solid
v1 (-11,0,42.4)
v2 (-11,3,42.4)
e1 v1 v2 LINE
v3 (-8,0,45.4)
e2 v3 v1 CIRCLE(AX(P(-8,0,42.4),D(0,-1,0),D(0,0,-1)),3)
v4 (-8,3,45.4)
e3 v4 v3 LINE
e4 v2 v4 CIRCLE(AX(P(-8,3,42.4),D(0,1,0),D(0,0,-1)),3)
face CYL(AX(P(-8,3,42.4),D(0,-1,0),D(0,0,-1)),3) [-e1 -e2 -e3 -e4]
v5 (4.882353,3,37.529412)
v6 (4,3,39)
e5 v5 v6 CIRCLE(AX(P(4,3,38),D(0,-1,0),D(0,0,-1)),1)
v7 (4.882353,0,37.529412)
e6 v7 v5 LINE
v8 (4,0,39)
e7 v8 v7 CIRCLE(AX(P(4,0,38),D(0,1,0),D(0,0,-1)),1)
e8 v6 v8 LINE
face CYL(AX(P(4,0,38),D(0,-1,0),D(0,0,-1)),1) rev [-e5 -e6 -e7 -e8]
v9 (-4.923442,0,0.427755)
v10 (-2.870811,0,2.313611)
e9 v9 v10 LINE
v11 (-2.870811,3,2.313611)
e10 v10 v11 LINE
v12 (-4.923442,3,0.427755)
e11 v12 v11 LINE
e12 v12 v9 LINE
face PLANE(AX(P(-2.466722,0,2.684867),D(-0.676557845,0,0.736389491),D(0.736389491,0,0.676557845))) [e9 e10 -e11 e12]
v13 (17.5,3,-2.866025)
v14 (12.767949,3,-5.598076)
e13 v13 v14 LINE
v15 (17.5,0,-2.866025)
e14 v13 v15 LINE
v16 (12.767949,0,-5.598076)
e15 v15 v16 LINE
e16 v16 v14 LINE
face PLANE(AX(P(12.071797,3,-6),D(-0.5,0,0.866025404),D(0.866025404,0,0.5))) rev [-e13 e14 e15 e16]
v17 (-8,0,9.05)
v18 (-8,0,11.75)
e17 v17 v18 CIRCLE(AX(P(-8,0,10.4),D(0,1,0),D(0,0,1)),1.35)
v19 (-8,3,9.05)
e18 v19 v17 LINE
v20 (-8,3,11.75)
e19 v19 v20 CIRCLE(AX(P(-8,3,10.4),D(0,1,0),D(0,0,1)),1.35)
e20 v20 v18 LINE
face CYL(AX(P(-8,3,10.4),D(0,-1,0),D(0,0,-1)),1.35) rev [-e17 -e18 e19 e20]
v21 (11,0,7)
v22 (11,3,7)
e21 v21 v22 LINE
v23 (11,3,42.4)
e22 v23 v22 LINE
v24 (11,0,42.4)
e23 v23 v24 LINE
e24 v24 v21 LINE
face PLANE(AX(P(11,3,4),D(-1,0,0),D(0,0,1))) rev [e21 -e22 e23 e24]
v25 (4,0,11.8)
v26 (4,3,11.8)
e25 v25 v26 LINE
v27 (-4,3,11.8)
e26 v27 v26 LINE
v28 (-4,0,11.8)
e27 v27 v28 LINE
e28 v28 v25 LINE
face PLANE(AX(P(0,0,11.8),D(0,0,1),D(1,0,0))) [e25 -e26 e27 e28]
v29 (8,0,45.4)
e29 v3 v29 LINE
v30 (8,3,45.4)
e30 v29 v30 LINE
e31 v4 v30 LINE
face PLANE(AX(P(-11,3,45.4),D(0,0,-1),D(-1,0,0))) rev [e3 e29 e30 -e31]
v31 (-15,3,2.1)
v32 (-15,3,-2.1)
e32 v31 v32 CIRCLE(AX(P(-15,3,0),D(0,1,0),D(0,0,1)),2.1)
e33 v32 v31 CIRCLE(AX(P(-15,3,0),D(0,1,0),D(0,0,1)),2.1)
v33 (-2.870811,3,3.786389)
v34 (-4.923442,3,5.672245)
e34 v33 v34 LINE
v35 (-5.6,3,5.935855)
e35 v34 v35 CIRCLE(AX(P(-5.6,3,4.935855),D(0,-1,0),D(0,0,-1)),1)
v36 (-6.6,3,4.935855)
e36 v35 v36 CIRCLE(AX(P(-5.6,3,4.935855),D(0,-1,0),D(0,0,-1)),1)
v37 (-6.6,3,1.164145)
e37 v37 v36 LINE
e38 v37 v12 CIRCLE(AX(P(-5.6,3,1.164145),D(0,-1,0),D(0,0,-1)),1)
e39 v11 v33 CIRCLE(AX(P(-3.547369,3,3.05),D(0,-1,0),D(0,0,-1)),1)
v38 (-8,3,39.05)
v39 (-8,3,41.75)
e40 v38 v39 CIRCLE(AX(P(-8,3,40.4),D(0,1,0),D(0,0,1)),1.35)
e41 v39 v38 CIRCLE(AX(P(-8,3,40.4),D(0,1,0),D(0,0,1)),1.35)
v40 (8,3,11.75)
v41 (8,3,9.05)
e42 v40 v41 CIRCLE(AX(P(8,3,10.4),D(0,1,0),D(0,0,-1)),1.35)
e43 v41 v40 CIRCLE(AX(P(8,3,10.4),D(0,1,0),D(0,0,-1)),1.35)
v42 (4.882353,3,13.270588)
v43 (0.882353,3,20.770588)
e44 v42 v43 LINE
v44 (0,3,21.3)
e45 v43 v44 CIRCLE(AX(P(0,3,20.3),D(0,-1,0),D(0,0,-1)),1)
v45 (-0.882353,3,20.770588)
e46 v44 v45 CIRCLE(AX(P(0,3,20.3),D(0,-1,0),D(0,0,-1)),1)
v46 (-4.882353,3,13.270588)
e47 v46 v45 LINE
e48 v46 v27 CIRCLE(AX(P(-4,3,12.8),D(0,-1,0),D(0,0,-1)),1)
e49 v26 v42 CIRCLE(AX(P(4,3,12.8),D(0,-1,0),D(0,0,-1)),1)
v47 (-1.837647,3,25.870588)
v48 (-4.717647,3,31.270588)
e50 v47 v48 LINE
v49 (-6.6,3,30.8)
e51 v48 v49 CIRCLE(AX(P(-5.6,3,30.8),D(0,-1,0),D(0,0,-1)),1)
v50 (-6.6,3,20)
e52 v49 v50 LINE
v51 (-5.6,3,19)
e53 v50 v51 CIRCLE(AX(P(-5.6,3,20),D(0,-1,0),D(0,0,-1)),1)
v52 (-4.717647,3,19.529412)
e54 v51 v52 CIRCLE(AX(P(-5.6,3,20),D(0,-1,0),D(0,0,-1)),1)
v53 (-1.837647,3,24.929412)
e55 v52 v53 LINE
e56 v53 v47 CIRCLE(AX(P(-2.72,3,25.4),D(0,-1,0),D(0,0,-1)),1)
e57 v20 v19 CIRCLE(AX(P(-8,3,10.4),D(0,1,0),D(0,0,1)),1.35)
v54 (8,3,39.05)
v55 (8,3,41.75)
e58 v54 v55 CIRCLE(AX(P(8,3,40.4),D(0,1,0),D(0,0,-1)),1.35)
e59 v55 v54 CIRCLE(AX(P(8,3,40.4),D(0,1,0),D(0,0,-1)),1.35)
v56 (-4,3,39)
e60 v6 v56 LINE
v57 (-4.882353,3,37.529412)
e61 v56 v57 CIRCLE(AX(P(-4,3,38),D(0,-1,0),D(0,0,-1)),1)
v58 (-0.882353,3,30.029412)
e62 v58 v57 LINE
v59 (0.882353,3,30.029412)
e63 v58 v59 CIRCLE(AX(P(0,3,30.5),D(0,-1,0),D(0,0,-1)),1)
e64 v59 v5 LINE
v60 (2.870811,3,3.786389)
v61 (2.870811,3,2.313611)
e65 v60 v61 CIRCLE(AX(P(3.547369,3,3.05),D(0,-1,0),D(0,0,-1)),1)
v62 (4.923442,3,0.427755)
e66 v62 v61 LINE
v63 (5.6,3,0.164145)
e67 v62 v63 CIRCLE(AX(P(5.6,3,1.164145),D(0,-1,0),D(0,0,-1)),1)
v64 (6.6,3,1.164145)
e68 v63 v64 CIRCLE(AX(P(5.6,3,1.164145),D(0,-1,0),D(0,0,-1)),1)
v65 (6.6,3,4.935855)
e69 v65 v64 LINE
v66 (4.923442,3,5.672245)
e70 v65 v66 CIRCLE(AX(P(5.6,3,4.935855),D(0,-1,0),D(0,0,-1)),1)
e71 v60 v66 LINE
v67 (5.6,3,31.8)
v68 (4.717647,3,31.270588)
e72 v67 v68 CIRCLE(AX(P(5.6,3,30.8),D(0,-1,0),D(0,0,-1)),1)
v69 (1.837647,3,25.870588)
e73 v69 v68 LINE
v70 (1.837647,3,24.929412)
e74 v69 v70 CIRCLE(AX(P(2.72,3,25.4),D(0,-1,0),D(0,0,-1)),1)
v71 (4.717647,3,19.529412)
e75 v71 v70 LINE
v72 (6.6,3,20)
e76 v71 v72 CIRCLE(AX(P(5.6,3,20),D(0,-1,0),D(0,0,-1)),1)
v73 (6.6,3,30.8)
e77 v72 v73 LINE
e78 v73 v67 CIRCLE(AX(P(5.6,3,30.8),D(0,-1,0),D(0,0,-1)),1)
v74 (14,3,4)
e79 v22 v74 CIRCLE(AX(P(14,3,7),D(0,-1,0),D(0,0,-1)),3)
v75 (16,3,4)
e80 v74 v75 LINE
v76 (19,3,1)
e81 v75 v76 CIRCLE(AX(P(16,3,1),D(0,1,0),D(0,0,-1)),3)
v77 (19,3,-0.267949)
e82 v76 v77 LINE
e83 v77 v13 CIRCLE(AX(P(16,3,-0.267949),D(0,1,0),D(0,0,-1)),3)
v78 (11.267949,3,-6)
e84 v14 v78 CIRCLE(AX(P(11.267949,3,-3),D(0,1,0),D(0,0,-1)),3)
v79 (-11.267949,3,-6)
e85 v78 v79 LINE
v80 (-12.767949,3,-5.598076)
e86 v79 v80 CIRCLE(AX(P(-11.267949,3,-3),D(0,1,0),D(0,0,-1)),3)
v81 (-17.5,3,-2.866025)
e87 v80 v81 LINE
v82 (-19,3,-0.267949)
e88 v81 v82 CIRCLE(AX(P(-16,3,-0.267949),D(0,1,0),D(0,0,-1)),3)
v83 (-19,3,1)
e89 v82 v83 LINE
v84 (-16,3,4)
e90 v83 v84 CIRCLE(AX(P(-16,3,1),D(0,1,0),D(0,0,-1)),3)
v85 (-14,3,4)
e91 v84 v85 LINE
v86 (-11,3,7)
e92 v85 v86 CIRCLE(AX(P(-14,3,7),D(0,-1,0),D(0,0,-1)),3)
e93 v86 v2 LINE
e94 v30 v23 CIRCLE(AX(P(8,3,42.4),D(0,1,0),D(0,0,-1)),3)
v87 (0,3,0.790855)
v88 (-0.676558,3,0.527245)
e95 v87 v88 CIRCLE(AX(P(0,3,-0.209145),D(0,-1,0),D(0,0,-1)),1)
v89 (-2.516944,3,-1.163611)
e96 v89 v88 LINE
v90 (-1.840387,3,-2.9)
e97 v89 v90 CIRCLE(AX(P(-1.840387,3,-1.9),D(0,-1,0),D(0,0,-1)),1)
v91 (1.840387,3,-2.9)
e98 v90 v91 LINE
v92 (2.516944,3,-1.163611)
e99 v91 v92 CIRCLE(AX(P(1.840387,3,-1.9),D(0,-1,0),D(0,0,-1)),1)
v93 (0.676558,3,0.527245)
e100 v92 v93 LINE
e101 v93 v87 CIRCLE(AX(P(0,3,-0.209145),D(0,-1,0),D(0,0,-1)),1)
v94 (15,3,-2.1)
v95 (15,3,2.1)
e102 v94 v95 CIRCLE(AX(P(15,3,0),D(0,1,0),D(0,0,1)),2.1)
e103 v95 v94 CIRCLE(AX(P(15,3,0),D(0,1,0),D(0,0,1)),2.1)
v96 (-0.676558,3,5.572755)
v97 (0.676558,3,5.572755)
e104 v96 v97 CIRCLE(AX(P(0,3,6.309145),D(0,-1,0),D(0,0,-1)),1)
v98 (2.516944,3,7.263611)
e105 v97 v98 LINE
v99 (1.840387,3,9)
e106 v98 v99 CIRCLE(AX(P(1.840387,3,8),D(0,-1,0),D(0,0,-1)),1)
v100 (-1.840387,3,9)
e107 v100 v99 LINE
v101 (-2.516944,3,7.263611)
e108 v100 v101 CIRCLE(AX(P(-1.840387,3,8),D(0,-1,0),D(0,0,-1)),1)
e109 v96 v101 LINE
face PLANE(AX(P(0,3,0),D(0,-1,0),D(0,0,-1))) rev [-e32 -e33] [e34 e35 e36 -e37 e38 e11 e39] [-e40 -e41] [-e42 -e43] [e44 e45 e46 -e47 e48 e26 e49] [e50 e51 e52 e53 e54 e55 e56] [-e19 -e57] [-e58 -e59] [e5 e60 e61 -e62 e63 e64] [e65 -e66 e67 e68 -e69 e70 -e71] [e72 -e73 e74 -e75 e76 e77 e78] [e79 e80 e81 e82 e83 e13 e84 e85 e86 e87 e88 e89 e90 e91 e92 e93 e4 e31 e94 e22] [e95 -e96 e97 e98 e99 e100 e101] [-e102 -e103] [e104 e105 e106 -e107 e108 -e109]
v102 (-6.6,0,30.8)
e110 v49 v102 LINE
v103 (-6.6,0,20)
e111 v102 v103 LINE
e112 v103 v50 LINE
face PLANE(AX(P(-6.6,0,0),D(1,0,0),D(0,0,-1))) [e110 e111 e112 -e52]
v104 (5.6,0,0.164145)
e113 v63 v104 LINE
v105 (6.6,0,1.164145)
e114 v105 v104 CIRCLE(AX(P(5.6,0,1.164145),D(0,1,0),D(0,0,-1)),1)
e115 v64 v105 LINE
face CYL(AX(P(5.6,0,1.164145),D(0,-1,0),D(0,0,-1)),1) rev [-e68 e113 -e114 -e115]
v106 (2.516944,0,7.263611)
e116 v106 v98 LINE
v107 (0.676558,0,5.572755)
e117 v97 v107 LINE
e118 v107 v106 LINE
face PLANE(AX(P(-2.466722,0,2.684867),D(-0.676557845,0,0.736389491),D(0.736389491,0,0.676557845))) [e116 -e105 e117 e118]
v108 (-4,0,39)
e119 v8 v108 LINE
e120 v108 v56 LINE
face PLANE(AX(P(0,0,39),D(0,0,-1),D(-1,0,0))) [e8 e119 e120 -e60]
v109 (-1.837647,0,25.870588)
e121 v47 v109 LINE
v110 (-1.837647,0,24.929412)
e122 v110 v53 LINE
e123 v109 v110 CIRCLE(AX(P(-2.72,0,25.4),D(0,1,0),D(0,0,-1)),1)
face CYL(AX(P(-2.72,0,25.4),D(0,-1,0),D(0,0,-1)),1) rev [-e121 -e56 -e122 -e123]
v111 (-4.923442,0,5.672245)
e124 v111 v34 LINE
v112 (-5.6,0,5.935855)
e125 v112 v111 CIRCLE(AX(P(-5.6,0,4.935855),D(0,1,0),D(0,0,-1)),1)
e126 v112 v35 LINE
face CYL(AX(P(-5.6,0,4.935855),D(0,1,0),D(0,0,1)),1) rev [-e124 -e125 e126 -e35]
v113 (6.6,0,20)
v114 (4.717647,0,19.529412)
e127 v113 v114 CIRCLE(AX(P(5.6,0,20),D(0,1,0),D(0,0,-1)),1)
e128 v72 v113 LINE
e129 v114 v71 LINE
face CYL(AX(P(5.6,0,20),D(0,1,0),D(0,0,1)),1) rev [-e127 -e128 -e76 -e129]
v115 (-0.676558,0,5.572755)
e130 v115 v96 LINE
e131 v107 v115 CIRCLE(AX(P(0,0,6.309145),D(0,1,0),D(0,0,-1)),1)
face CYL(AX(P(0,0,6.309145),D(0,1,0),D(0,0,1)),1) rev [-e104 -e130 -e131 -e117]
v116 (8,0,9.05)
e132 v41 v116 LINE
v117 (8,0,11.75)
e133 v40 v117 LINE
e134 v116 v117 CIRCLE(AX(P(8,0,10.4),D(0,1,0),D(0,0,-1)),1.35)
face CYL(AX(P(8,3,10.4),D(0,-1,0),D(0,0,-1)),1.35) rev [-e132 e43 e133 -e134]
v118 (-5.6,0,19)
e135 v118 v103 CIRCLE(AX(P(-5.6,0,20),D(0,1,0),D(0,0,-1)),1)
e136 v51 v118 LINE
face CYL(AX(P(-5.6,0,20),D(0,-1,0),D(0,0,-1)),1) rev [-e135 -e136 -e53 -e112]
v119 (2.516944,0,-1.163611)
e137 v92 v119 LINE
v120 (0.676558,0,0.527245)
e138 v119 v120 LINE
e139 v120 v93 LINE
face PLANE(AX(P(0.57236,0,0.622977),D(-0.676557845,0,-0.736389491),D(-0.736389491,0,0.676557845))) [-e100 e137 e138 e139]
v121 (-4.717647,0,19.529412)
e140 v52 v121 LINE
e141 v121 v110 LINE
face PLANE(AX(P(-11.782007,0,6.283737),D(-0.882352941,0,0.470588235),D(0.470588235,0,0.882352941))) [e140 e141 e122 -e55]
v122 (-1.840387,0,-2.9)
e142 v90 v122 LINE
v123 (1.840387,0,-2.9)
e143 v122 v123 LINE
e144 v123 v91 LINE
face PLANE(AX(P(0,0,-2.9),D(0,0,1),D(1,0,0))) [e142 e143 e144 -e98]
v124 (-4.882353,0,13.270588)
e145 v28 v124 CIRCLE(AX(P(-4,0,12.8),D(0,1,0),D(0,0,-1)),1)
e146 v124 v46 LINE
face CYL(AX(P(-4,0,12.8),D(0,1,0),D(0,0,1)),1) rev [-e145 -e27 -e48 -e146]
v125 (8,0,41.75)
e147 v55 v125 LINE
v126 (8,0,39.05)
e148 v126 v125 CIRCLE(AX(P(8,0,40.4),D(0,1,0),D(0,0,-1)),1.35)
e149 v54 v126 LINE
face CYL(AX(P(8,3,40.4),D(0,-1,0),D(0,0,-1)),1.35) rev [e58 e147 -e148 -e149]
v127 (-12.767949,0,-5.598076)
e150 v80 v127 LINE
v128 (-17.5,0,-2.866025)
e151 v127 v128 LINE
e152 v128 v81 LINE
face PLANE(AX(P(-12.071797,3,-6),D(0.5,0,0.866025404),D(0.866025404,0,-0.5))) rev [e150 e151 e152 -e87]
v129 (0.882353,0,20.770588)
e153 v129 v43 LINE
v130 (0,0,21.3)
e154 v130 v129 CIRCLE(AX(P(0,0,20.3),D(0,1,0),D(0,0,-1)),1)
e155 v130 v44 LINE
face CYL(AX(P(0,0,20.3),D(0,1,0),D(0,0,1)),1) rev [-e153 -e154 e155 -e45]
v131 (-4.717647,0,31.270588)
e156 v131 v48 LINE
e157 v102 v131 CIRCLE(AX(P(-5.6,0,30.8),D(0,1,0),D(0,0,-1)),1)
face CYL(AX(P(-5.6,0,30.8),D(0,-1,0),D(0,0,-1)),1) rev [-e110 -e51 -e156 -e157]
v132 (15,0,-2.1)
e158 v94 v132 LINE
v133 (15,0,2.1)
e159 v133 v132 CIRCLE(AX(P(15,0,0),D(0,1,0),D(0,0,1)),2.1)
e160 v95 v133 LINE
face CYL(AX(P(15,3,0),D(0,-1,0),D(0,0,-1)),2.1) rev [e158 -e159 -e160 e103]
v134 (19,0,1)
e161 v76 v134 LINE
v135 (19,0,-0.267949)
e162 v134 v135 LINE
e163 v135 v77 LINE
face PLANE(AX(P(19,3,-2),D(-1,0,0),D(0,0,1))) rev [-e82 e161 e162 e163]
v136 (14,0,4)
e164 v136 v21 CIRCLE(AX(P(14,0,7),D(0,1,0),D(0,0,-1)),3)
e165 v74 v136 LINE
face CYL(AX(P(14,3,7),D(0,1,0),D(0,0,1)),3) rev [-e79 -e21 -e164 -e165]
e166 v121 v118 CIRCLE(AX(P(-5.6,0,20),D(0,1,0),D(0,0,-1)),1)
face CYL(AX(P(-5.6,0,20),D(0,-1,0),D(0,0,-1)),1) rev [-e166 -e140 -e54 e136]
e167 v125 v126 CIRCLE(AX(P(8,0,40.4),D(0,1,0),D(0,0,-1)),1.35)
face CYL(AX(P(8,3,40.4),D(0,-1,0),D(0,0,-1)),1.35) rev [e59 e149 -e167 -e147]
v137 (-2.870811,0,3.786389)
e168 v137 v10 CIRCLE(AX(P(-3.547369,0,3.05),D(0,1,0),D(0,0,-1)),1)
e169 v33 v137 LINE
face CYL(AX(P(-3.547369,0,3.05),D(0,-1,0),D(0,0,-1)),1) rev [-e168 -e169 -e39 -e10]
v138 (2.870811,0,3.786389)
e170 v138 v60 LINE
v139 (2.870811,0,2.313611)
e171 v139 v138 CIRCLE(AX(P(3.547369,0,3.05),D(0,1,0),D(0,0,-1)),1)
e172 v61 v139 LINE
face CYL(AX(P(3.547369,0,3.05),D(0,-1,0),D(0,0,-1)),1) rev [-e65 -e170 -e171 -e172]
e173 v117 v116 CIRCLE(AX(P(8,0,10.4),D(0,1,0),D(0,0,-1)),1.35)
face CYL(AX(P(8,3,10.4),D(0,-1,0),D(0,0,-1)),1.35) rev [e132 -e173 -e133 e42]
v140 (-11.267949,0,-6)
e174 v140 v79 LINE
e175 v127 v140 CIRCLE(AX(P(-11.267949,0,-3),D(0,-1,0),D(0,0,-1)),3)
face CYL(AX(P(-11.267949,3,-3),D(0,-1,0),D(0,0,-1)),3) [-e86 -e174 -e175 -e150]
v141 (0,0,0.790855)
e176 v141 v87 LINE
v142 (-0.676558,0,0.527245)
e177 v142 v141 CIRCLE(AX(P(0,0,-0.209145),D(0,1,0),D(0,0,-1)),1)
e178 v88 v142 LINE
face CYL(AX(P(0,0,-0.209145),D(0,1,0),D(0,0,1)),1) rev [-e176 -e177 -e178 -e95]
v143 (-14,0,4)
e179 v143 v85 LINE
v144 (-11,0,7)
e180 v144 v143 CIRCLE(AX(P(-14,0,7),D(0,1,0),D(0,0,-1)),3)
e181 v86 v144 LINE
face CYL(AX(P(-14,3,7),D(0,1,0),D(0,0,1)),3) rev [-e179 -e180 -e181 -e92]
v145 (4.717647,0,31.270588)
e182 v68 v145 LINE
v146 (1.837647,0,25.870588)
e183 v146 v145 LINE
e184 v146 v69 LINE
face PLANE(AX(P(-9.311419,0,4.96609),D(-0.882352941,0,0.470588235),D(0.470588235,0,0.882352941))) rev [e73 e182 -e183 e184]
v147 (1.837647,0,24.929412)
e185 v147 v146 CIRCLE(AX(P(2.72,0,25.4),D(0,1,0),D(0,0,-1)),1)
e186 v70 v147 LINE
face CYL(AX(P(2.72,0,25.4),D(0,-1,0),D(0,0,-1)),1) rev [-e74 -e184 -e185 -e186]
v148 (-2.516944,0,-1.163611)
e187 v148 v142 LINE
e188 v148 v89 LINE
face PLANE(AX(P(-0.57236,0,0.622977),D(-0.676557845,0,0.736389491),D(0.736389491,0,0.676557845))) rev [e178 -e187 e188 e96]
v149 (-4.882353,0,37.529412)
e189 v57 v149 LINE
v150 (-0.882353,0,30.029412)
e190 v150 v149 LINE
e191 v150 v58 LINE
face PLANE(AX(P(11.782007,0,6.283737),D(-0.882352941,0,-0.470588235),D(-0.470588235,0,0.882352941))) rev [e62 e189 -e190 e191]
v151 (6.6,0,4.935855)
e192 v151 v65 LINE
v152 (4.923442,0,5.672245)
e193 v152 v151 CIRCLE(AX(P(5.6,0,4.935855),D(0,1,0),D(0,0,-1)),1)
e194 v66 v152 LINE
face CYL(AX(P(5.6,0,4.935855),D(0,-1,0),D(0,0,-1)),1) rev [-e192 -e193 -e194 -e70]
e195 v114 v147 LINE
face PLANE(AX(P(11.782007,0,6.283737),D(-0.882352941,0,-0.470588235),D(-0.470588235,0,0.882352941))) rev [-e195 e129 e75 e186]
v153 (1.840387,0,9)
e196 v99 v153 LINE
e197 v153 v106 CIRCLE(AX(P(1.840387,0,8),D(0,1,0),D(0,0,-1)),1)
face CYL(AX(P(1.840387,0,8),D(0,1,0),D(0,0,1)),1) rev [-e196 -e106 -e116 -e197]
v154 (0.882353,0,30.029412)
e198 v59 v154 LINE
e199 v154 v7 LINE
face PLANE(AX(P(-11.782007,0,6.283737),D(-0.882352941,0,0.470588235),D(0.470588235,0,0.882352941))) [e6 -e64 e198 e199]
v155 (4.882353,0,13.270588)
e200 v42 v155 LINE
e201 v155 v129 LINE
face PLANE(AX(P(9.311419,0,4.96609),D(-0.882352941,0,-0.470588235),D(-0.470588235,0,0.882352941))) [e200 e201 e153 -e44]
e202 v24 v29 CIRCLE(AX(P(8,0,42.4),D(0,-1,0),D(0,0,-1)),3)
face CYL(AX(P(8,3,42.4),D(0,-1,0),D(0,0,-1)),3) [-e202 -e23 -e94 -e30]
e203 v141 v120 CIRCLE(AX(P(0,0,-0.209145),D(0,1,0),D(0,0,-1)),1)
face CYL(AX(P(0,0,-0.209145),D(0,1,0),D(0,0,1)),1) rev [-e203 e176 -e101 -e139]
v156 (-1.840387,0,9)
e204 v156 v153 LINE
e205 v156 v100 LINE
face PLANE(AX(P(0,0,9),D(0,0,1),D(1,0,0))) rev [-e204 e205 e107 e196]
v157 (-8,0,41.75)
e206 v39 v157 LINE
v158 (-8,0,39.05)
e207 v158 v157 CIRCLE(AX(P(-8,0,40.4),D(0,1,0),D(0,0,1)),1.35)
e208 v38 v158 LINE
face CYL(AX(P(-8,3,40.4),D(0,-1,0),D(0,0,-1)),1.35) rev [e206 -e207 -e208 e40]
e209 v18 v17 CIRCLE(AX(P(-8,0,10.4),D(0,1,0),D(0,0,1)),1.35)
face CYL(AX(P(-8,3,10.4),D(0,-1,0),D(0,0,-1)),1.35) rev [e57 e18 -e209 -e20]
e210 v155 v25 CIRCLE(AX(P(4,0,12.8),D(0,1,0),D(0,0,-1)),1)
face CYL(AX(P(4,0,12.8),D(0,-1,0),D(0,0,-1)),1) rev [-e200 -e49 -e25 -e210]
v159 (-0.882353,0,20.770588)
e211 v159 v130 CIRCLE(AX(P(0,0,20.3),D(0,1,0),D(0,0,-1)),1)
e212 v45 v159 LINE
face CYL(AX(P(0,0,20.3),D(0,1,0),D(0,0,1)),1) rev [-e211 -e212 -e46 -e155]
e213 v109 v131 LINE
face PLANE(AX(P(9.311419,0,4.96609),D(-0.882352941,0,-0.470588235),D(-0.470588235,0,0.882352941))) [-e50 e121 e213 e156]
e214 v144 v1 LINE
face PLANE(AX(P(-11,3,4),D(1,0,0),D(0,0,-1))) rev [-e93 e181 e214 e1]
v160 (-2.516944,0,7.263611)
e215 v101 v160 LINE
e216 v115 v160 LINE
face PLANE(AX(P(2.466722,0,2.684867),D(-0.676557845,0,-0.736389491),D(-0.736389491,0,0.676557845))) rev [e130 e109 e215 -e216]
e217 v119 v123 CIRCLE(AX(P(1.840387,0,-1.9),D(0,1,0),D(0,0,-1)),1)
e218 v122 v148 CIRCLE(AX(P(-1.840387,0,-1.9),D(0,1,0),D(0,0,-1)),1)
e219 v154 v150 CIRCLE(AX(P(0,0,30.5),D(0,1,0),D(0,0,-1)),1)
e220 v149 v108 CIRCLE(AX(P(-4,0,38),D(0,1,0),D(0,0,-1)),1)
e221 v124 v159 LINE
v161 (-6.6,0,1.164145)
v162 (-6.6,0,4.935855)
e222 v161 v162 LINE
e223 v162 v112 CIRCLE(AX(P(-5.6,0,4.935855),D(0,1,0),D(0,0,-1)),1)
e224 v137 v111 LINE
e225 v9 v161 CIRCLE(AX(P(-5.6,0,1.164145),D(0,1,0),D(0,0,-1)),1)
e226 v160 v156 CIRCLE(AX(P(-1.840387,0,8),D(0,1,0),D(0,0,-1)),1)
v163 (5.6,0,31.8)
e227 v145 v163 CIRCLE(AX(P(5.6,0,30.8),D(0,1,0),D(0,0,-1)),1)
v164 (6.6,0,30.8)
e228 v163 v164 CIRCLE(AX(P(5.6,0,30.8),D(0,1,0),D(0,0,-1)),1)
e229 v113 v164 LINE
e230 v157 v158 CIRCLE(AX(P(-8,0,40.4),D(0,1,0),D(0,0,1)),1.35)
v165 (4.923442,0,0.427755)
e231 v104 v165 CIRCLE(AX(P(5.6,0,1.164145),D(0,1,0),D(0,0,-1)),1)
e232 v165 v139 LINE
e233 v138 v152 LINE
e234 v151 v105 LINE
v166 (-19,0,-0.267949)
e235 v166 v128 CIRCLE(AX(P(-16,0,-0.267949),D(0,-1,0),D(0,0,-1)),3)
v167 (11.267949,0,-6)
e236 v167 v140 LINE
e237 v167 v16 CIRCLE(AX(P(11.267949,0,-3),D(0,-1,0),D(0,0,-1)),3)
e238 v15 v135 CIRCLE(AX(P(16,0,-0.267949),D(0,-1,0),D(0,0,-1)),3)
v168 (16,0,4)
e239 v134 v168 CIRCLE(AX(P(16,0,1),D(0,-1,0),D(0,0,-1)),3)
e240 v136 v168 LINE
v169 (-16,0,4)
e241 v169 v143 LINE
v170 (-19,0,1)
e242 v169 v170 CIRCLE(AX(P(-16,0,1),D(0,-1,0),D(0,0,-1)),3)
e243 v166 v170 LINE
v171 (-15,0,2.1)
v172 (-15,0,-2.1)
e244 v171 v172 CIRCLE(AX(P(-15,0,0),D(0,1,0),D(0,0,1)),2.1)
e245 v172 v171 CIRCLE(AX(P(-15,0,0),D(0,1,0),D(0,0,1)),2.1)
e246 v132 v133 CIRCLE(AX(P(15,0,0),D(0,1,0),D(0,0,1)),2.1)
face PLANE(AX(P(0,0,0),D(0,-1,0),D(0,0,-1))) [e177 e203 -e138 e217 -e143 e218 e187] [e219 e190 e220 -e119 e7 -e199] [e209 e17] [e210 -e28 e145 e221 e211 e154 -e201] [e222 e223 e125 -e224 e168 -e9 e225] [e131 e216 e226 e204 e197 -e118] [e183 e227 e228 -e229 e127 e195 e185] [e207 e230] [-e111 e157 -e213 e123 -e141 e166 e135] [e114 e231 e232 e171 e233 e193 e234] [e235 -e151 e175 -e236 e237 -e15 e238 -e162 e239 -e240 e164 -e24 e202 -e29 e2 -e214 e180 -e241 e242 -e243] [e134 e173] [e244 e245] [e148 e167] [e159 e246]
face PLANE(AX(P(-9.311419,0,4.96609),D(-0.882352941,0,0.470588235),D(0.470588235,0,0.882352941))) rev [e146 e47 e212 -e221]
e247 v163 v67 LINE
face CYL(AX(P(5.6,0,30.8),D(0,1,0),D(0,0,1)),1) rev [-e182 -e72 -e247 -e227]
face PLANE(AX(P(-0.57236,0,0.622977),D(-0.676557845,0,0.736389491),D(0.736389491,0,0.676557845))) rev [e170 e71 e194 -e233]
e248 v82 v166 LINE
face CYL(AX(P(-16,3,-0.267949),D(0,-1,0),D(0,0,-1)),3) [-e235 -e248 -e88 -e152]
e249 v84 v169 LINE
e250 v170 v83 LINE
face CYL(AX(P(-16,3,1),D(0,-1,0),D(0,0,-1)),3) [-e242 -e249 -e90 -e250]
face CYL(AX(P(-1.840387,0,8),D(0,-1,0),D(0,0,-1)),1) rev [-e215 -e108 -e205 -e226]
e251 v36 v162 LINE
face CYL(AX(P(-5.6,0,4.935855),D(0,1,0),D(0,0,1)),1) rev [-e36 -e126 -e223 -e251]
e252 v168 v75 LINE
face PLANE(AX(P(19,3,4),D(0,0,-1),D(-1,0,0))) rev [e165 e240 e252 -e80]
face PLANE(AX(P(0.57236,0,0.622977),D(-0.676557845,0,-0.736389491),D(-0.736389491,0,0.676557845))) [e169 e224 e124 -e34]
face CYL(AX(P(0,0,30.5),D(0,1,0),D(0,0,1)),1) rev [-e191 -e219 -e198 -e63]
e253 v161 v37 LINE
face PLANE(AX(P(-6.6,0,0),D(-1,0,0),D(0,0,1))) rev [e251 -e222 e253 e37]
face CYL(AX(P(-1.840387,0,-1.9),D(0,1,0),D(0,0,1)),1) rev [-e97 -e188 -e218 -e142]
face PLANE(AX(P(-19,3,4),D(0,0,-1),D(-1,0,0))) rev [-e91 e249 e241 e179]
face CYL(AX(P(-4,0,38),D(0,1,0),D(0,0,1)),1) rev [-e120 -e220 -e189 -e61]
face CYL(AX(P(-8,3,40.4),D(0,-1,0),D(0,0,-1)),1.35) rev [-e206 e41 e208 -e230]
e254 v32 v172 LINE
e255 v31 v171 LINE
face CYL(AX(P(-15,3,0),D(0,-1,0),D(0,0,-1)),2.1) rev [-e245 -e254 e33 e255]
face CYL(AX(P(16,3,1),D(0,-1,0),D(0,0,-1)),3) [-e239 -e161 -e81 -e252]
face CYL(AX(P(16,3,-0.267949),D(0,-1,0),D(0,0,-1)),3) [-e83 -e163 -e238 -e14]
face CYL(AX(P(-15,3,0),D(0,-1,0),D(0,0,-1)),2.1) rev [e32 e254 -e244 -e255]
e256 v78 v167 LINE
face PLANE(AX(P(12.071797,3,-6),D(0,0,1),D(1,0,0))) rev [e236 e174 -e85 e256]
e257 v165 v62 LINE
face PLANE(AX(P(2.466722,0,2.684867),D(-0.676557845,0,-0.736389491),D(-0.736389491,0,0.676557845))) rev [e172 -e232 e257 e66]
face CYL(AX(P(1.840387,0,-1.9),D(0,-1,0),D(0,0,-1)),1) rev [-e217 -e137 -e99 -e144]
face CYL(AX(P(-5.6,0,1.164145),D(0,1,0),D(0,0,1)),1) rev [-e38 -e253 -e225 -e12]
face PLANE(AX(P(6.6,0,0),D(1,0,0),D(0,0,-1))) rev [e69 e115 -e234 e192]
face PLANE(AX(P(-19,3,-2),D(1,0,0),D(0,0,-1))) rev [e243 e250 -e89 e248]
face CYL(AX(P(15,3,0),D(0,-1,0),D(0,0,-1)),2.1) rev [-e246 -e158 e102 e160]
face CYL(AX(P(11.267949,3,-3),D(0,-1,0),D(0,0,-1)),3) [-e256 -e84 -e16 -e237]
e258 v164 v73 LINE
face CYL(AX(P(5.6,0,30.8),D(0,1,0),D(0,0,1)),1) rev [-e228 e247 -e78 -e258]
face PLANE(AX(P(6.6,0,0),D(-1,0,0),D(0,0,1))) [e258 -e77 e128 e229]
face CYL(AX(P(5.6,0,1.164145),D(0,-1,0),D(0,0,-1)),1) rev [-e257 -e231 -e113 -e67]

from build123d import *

# Parameters (mm, degrees)
SKETCH1_R              = 2.1
SKETCH1_R_2            = 1.35
BOSS_EXTRUDE1_DEPTH    = 3
CUT_EXTRUDE1_DEPTH     = 50.306794664
R3_OUTER_EDGE_FILLET_R = 3
R1_CUTOUT_FILLET_R     = 1


with BuildPart() as part:
    # Sketch1 → Boss-Extrude1 (new body)
    with BuildSketch(Plane(origin=(0, 0, 0), x_dir=(1, 0, 0), z_dir=(0, 1, 0))):
        Polygon((-12.07179677, 6), (-19, 2), (-19, -4), (-11, -4), (-11, -45.4), (11, -45.4), (11, -4), (19, -4), (19, 2), (12.07179677, 6), align=None)
        with Locations(Location((-15, 0, 0), (0, 0, 270))):
            Circle(SKETCH1_R, mode=Mode.SUBTRACT)
        with Locations(Location((15, 0, 0), (0, 0, 270))):
            Circle(SKETCH1_R, mode=Mode.SUBTRACT)
        with Locations(Location((-8, -10.4, 0), (0, 0, 270))):
            Circle(SKETCH1_R_2, mode=Mode.SUBTRACT)
        with Locations(Location((-8, -40.4, 0), (0, 0, 270))):
            Circle(SKETCH1_R_2, mode=Mode.SUBTRACT)
        with Locations(Location((8, -10.4, 0), (0, 0, 90))):
            Circle(SKETCH1_R_2, mode=Mode.SUBTRACT)
        with Locations(Location((8, -40.4, 0), (0, 0, 90))):
            Circle(SKETCH1_R_2, mode=Mode.SUBTRACT)
    extrude(amount=BOSS_EXTRUDE1_DEPTH)

    # Sketch2 → Cut-Extrude1 (cut, through all)
    with BuildSketch(Plane(origin=(0, 3, 0), x_dir=(1, 0, 0), z_dir=(0, 1, 0))):
        Polygon((-6.6, 1.112582185), (-6.6, -7.212582185), (-2.069298303, -3.05), align=None)
        Polygon((-4.406892174, 2.9), (0, -1.148832185), (4.406892174, 2.9), align=None)
        Polygon((6.6, 1.112582185), (2.069298303, -3.05), (6.6, -7.212582185), align=None)
        Polygon((0, -4.951167815), (-4.406892174, -9), (4.406892174, -9), align=None)
        Polygon((5.666666667, -11.8), (-5.666666667, -11.8), (0, -22.425), align=None)
        Polygon((-1.586666667, -25.4), (-6.6, -16), (-6.6, -34.8), align=None)
        Polygon((5.666666667, -39), (0, -28.375), (-5.666666667, -39), align=None)
        Polygon((6.6, -16), (1.586666667, -25.4), (6.6, -34.8), align=None)
    extrude(amount=-CUT_EXTRUDE1_DEPTH, mode=Mode.SUBTRACT)

    # R3 outer edge fillet
    r3_outer_edge_fillet_edges = [part.edges().sort_by_distance(p)[0] for p in [
        (19, 1.5, 4),
        (11, 1.5, 4),
        (11, 1.5, 45.4),
        (-11, 1.5, 45.4),
        (-11, 1.5, 4),
        (-19, 1.5, 4),
        (-19, 1.5, -2),
        (-12.07179677, 1.5, -6),
        (12.07179677, 1.5, -6),
        (19, 1.5, -2),
    ]]
    fillet(r3_outer_edge_fillet_edges, radius=R3_OUTER_EDGE_FILLET_R)

    # R1 cutout fillet
    r1_cutout_fillet_edges = [part.edges().sort_by_distance(p)[0] for p in [
        (6.6, 1.5, 16),
        (6.6, 1.5, 34.8),
        (1.586666667, 1.5, 25.4),
        (-6.6, 1.5, 34.8),
        (-6.6, 1.5, 16),
        (-1.586666667, 1.5, 25.4),
        (5.666666667, 1.5, 39),
        (-5.666666667, 1.5, 39),
        (0, 1.5, 28.375),
        (-2.069298303, 1.5, 3.05),
        (-6.6, 1.5, 7.212582185),
        (-6.6, 1.5, -1.112582185),
        (-5.666666667, 1.5, 11.8),
        (5.666666667, 1.5, 11.8),
        (0, 1.5, 22.425),
        (0, 1.5, 4.951167815),
        (4.406892174, 1.5, 9),
        (-4.406892174, 1.5, 9),
        (4.406892174, 1.5, -2.9),
        (0, 1.5, 1.148832185),
        (-4.406892174, 1.5, -2.9),
        (6.6, 1.5, -1.112582185),
        (6.6, 1.5, 7.212582185),
        (2.069298303, 1.5, 3.05),
    ]]
    fillet(r1_cutout_fillet_edges, radius=R1_CUTOUT_FILLET_R)


solid = part.part
